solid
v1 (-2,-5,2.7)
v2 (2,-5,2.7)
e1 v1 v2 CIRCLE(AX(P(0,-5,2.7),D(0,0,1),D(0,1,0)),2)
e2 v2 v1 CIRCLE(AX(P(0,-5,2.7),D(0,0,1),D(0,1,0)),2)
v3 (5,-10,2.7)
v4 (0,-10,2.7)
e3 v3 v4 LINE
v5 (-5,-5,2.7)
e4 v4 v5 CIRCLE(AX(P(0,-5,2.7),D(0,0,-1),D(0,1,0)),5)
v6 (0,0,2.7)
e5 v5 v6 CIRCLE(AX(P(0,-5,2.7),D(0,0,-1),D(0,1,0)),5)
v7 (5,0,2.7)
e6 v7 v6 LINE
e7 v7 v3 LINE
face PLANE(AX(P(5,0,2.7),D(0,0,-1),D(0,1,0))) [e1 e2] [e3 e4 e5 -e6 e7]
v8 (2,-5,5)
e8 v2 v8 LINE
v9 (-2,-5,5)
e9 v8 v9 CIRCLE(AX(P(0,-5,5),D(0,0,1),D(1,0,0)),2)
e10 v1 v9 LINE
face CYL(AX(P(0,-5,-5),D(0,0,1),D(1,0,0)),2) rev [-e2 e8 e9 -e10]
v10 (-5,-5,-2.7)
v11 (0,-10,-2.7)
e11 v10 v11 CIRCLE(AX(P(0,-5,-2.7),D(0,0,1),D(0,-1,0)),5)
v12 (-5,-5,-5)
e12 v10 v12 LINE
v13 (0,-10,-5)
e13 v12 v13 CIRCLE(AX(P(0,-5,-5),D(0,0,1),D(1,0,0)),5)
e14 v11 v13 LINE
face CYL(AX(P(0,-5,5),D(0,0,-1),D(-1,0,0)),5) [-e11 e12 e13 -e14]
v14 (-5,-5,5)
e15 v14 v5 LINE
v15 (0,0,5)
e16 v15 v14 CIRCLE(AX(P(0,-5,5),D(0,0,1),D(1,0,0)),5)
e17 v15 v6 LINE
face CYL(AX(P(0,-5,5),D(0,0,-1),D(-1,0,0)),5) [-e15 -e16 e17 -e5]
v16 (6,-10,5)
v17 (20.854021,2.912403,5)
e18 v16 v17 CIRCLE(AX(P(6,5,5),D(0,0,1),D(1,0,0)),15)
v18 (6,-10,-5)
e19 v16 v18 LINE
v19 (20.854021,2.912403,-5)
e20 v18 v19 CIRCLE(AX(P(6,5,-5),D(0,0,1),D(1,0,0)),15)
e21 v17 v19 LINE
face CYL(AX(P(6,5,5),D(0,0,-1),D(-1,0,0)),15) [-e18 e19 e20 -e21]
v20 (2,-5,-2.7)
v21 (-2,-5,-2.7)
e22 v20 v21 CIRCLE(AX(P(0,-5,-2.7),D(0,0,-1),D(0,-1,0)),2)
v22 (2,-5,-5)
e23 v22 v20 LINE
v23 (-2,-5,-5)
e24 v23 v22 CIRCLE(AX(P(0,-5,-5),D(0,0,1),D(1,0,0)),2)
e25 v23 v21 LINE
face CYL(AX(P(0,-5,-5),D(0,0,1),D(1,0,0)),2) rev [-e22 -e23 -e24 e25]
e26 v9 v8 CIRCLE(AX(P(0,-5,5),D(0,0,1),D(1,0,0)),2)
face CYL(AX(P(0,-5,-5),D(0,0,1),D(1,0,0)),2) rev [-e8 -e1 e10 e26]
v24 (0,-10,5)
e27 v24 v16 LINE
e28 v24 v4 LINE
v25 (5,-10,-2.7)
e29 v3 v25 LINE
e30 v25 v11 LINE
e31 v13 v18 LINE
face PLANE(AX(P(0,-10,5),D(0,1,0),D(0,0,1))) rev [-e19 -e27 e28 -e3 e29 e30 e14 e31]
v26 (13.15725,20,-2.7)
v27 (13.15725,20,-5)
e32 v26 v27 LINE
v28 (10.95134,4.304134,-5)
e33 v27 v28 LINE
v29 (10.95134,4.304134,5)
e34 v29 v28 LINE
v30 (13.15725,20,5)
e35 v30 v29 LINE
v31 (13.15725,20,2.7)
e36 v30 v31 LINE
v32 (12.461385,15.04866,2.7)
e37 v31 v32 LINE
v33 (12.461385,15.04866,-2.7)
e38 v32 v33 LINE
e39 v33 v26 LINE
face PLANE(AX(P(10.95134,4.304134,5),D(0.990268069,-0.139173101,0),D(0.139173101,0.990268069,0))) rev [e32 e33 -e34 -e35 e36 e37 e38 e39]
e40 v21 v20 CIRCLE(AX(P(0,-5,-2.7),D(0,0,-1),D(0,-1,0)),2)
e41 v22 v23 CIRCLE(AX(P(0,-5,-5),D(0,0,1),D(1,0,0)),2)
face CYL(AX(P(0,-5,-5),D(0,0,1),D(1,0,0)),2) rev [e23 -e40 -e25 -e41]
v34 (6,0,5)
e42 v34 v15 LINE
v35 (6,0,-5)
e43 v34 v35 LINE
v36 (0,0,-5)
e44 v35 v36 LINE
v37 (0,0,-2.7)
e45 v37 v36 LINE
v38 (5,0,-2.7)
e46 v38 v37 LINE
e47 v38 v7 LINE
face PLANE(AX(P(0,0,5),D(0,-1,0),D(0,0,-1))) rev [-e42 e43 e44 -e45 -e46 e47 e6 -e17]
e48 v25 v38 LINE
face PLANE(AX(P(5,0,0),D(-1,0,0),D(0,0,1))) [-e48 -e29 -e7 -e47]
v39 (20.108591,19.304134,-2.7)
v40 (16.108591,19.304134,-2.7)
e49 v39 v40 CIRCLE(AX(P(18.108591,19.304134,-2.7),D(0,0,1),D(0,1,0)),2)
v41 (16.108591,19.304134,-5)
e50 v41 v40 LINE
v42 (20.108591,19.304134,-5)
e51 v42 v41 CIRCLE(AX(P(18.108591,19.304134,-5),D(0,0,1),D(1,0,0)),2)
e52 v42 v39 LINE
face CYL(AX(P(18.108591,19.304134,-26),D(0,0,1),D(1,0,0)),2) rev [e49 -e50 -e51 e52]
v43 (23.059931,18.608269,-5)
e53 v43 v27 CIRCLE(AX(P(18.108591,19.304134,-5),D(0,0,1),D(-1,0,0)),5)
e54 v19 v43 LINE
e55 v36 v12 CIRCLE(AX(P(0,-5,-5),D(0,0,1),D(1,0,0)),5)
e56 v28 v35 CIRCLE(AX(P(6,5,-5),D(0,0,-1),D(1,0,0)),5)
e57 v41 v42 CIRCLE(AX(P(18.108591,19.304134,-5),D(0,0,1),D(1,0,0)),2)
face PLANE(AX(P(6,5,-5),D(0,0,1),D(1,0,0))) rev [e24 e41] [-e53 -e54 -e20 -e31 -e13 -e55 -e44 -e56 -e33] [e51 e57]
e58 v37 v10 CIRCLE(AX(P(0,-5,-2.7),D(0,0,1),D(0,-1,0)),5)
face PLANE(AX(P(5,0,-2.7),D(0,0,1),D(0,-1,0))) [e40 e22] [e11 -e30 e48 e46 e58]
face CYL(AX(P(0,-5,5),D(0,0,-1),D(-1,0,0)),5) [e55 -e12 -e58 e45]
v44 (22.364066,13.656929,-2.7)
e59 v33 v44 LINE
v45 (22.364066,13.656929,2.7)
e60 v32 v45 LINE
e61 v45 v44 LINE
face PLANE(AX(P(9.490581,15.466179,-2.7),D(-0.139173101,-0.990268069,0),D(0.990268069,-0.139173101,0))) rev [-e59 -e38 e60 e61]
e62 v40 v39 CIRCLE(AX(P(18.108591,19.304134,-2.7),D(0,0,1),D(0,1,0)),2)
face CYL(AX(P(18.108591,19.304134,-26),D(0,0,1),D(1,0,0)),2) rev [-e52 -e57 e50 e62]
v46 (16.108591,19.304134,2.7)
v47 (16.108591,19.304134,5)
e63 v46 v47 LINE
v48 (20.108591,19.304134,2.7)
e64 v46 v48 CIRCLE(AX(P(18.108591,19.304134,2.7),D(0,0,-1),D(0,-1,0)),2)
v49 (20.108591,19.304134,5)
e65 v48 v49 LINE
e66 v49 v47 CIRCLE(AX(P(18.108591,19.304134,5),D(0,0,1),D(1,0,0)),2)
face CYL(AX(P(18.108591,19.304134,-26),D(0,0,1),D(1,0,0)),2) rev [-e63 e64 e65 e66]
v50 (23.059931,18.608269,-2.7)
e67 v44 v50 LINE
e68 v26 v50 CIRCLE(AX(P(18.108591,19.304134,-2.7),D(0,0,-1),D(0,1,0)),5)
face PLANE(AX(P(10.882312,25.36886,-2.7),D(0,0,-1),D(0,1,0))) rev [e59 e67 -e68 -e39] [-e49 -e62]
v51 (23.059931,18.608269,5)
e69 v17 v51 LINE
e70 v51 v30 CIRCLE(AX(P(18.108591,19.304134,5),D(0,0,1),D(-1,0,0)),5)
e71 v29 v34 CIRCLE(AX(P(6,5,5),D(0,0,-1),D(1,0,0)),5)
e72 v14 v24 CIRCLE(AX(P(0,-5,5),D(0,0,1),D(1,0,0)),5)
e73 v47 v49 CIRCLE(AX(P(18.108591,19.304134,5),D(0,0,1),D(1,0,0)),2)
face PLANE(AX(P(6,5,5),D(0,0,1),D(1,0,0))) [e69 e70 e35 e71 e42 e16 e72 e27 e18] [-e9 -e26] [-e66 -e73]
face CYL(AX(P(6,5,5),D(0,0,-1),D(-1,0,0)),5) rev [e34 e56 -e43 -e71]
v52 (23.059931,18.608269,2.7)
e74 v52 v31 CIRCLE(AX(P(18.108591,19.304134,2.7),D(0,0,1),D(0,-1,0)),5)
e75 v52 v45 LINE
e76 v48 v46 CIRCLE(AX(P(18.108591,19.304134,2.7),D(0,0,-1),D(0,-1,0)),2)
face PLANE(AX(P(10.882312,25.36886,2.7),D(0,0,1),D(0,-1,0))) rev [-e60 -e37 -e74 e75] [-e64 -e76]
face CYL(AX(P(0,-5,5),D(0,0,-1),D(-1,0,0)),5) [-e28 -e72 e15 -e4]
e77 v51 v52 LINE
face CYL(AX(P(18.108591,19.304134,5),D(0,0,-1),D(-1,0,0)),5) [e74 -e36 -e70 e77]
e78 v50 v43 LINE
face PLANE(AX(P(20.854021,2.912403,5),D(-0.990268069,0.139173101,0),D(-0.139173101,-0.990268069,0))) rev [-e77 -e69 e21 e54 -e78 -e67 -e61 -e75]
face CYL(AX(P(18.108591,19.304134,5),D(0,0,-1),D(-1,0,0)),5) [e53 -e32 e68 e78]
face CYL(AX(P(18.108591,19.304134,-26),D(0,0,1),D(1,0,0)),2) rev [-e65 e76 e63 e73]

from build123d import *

# Parameters (mm, degrees)
BOSS_EXTRUDE1_DEPTH     = 5
CUT_EXTRUDE1_DEPTH      = 34.907195681
CUT_EXTRUDE1_DEPTH_BACK = 34.907195681
SKETCH2_R               = 2
SKETCH3_W               = 5.4
SKETCH3_H               = 10
CUT_EXTRUDE2_DEPTH      = 10
SKETCH4_R               = 2
CUT_EXTRUDE3_DEPTH      = 31
SKETCH7_W               = 5.4
SKETCH7_H               = 10
CUT_EXTRUDE5_DEPTH      = 13


with BuildPart() as part:
    # Sketch1 → Boss-Extrude1 (new, symmetric)
    with BuildSketch(Plane.XY):
        with BuildLine():
            Line((10.951340344, 4.304134495), (13.157250383, 20))
            ThreePointArc((13.157250383, 20), (18.804456232, 24.255474839), (23.059931071, 18.60826899))
            Line((23.059931071, 18.60826899), (20.854021031, 2.912403486))
            ThreePointArc((20.854021031, 2.912403486), (15.840885435, -6.320643703), (6, -10))
            Line((6, -10), (0, -10))
            ThreePointArc((0, -10), (-5, -5), (0, 0))
            Line((0, 0), (6, 0))
            ThreePointArc((6, 0), (9.280295145, 1.226452099), (10.951340344, 4.304134495))
        make_face()
    extrude(amount=BOSS_EXTRUDE1_DEPTH, both=True)

    # Sketch2 → Cut-Extrude1 (cut, two sides: drawn at the far end of the back side and taken through both)
    with BuildSketch(Plane.XY.offset(-CUT_EXTRUDE1_DEPTH_BACK)):
        with Locations((0, -5)):
            Circle(SKETCH2_R)
    extrude(amount=CUT_EXTRUDE1_DEPTH + CUT_EXTRUDE1_DEPTH_BACK, mode=Mode.SUBTRACT)

    # Sketch3 → Cut-Extrude2 (cut)
    with BuildSketch(Plane(origin=(-5, 0, 0), x_dir=(0, 0, -1), z_dir=(1, 0, 0))):
        with Locations((0, -5)):
            Rectangle(SKETCH3_W, SKETCH3_H)
    extrude(amount=CUT_EXTRUDE2_DEPTH, mode=Mode.SUBTRACT)

    # Sketch4 → Cut-Extrude3 (cut)
    with BuildSketch(Plane.XY.offset(5)):
        with Locations((18.108590727, 19.304134495)):
            Circle(SKETCH4_R)
    extrude(amount=-CUT_EXTRUDE3_DEPTH, mode=Mode.SUBTRACT)

    # Sketch7 → Cut-Extrude5 (cut)
    with BuildSketch(Plane(origin=(20.048712729, -2.817662822, 0), x_dir=(0, 0, -1), z_dir=(0.9902680687415704, -0.13917310096006613, 0))):
        with Locations((0, 21.636496711)):
            Rectangle(SKETCH7_W, SKETCH7_H)
    extrude(amount=-CUT_EXTRUDE5_DEPTH, mode=Mode.SUBTRACT)


solid = part.part
